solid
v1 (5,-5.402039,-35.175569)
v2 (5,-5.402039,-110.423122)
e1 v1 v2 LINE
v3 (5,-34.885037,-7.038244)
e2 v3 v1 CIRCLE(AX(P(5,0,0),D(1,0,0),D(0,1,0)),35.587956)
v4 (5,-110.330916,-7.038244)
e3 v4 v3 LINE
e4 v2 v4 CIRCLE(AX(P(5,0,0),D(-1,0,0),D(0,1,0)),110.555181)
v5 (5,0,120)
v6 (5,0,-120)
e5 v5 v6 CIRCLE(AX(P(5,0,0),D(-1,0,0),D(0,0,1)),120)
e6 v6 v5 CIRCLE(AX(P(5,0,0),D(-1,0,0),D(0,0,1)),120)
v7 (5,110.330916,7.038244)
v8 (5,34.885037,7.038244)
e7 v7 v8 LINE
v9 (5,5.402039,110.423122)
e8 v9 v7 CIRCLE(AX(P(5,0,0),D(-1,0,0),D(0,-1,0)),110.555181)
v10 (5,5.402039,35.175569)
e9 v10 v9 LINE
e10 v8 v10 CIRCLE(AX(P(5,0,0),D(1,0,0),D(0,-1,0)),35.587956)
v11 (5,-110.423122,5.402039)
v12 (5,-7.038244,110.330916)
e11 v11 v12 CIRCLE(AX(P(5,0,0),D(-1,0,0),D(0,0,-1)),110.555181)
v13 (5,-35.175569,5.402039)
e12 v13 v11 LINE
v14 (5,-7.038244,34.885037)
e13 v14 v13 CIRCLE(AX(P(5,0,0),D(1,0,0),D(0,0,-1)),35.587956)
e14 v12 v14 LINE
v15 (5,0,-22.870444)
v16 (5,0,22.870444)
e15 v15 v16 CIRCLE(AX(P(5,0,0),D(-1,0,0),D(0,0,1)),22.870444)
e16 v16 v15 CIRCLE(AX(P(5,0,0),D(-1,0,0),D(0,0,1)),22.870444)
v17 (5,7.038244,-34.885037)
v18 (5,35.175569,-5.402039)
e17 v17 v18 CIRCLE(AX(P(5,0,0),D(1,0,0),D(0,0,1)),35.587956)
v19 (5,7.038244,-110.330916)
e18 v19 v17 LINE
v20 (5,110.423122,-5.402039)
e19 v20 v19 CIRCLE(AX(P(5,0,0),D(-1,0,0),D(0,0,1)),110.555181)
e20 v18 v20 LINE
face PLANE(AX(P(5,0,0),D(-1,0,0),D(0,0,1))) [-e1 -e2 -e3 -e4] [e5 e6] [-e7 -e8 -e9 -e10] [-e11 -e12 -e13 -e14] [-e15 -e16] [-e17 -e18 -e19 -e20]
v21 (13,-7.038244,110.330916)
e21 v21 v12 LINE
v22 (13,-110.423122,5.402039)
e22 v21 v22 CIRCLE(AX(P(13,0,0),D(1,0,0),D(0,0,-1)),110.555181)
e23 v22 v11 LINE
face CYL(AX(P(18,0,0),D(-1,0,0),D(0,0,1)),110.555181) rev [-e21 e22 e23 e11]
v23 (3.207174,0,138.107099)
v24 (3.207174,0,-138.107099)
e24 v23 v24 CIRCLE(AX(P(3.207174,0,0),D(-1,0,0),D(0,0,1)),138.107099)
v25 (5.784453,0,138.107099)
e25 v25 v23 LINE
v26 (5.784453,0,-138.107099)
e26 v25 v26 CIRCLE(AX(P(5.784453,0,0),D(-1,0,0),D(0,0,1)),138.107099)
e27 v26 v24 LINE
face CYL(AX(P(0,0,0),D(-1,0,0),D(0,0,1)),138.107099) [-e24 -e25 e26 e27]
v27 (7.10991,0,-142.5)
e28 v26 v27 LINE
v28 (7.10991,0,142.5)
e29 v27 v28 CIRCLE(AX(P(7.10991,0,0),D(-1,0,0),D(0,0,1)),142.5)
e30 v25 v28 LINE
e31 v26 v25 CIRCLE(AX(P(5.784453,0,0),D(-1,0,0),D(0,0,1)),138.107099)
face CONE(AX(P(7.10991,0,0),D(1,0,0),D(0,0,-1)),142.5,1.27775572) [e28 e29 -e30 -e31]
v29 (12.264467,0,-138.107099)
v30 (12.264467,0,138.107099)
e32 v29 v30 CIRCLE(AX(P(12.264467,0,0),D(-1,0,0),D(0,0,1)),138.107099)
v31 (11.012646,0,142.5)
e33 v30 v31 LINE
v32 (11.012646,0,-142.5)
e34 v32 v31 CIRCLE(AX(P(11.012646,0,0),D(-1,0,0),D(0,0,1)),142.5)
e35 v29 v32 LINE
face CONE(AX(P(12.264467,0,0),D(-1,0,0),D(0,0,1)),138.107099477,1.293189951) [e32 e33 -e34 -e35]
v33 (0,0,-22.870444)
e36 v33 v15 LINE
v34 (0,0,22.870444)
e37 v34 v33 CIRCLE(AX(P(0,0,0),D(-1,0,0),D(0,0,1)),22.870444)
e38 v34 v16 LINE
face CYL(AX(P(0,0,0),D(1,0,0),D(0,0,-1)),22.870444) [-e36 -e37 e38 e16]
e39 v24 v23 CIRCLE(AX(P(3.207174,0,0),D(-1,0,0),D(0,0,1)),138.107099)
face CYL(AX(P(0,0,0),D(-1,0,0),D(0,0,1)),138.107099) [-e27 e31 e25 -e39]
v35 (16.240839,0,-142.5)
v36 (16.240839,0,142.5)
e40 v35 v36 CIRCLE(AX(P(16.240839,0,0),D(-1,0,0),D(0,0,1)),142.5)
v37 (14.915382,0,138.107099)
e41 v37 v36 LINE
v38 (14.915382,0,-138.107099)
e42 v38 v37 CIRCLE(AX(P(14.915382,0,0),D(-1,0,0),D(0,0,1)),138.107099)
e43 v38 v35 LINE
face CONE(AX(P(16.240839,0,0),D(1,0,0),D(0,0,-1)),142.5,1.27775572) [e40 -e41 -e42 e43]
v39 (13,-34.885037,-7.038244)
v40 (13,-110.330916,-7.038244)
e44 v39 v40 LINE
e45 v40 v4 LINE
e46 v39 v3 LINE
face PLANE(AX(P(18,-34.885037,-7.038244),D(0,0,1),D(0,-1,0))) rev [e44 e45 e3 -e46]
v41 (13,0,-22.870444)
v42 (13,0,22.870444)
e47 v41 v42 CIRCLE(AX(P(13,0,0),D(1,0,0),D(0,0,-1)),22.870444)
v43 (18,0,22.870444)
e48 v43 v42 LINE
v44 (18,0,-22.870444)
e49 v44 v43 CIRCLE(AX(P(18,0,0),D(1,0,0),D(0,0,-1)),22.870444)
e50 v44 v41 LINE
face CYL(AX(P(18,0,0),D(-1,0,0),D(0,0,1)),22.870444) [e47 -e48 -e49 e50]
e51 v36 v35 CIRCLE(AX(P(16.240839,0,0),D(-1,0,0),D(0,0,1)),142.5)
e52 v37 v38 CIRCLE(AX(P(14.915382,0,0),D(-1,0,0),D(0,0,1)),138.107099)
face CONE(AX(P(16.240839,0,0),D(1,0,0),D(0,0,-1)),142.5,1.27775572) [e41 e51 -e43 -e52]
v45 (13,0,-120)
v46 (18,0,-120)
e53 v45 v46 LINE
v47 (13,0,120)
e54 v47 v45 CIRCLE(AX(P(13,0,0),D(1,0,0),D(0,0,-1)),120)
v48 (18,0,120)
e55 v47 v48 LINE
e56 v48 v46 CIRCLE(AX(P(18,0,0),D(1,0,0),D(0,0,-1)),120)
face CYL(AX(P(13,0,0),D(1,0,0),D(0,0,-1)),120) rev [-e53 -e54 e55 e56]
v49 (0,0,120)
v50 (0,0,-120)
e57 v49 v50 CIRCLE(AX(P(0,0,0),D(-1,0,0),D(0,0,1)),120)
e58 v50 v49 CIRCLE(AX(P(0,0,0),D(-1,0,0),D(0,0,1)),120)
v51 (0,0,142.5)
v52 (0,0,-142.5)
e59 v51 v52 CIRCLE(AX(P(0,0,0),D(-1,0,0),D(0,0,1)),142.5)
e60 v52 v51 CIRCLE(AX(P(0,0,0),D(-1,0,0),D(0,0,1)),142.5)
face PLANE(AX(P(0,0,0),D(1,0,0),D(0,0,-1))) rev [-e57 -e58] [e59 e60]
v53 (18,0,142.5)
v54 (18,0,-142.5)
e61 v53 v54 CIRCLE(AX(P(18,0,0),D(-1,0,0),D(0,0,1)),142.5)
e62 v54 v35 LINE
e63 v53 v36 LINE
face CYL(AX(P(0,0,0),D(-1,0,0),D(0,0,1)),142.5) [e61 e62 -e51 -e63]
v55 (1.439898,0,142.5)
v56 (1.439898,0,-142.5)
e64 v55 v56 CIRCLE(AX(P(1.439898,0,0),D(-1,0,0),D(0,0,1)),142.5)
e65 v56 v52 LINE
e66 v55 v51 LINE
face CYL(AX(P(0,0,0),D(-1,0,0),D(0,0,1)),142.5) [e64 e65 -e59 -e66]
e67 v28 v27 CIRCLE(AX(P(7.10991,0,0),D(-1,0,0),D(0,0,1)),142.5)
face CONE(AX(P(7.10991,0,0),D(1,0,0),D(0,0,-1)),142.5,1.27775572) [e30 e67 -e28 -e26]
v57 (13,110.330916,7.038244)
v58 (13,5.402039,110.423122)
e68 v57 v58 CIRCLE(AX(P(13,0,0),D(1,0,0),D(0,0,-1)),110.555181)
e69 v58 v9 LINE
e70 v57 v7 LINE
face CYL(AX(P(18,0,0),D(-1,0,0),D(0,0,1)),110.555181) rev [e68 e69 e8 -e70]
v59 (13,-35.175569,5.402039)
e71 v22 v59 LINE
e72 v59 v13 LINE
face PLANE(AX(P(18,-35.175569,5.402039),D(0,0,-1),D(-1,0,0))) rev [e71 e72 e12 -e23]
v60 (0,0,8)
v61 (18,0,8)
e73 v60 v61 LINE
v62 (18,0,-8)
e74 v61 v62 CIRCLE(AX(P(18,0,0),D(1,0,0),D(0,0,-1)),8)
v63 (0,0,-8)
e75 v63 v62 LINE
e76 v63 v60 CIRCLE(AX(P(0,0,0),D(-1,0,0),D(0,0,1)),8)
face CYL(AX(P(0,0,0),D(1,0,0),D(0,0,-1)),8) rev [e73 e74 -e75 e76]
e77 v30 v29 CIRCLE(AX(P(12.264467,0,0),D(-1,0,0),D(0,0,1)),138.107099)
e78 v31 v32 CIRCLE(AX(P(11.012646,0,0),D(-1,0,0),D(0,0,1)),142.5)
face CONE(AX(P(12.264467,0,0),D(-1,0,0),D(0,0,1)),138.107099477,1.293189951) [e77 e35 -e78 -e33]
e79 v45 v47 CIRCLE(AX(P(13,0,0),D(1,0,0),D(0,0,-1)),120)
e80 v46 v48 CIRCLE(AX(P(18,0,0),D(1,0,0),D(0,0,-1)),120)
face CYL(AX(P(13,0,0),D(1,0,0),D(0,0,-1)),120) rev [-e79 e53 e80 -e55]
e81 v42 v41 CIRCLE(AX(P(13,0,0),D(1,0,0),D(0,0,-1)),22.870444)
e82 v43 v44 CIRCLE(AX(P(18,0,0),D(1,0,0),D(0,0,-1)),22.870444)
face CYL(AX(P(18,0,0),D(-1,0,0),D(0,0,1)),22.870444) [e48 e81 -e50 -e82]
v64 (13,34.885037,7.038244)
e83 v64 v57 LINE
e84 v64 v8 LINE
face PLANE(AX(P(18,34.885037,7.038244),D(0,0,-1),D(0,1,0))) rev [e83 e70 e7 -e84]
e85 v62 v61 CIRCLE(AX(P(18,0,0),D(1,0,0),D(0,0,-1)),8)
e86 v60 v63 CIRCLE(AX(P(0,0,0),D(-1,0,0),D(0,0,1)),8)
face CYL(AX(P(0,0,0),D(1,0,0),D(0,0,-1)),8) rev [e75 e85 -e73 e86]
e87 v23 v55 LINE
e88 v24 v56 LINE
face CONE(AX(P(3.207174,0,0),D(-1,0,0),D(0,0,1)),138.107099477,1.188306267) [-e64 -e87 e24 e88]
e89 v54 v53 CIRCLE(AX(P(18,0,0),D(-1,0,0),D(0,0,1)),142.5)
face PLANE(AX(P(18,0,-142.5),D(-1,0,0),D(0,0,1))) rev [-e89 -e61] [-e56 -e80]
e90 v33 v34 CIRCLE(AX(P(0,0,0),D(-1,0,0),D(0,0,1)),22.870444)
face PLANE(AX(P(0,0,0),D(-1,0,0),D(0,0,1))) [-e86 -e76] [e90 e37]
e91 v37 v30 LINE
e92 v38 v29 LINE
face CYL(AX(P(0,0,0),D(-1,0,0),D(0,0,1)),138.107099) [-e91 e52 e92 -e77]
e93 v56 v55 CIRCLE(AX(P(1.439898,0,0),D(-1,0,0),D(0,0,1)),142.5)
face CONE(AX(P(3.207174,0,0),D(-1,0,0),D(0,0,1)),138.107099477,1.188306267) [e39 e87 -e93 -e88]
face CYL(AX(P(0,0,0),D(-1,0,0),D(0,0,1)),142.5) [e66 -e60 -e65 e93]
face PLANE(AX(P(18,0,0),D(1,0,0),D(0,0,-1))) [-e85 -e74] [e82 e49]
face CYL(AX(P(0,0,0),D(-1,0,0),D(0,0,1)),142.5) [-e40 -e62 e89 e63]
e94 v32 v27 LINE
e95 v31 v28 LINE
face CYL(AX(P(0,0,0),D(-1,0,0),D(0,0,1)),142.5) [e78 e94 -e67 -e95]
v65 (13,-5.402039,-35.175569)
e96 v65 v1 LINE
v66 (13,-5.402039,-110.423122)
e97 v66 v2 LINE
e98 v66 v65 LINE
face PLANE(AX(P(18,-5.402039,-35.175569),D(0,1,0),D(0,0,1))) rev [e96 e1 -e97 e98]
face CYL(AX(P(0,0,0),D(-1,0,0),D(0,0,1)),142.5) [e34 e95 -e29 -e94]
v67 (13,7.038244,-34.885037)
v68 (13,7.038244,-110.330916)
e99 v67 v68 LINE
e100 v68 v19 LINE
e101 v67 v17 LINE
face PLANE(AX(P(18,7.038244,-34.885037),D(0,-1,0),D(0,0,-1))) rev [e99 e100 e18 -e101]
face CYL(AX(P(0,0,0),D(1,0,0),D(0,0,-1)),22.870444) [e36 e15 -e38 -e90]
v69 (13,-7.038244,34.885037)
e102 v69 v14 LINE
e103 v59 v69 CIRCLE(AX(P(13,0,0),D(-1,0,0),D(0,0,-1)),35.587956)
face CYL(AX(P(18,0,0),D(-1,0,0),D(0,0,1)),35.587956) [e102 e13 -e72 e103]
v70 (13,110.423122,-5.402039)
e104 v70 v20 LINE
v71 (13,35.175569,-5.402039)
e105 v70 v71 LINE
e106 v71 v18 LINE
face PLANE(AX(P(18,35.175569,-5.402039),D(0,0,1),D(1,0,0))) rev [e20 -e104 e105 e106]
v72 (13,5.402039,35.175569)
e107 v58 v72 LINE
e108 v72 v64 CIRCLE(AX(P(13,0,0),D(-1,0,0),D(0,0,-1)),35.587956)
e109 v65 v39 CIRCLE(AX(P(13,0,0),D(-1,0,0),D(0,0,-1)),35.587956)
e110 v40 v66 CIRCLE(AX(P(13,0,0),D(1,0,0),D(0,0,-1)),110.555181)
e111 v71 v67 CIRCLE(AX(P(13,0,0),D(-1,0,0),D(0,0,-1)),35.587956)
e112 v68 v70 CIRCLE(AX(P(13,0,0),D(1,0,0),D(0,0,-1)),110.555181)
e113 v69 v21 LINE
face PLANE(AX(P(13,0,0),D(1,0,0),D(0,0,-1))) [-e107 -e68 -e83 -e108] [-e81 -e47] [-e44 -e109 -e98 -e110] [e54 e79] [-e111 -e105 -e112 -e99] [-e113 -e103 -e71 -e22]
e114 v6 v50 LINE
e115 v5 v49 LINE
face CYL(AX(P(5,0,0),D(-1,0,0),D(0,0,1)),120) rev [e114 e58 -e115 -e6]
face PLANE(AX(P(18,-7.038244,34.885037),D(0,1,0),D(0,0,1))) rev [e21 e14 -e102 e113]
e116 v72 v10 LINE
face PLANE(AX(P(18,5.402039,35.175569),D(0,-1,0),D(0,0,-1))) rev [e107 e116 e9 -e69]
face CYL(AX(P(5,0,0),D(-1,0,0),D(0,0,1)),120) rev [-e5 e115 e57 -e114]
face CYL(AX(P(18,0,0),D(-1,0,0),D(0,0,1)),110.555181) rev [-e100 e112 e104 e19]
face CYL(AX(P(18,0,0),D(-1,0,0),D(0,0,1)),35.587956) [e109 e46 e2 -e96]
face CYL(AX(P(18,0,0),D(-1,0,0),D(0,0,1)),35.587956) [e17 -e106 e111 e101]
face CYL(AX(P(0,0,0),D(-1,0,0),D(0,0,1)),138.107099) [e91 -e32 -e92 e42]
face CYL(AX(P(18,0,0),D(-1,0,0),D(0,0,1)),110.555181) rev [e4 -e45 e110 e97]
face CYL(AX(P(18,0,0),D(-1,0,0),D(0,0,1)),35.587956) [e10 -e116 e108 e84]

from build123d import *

# Parameters (mm, degrees)
SKETCH2_R           = 120
CUT_EXTRUDE1_DEPTH  = 5
CUT_EXTRUDE2_START  = -5
SKETCH3_R           = 120
CUT_EXTRUDE2_DEPTH  = 5
SKETCH4_R           = 8
CUT_EXTRUDE3_DEPTH  = 202.944299251
BOSS_EXTRUDE1_START = 5
SKETCH5_R           = 22.870444207
SKETCH5_R_2         = 8
BOSS_EXTRUDE1_DEPTH = 5
SKETCH6_R           = 22.870444207
SKETCH6_R_2         = 8
BOSS_EXTRUDE2_DEPTH = 5
CUT_EXTRUDE5_DEPTH  = 202.944299251
CIRPATTERN1_COUNT   = 4


with BuildPart() as part:
    # Sketch1 → Revolve1 (revolve)
    with BuildSketch(Plane(origin=(0, 0, 0), x_dir=(1, 0, 0), z_dir=(0, 1, 0)), mode=Mode.PRIVATE) as revolve1_sk:
        Polygon((0, 0), (0, 142.5), (1.439897502, 142.5), (3.207174134, 138.107099477), (5.784452556, 138.107099477), (7.10991003, 142.5), (11.012645925, 142.5), (12.264466873, 138.107099477), (14.915381821, 138.107099477), (16.240839295, 142.5), (18, 142.5), (18, 0), align=None)
    revolve(revolve1_sk.sketch.rotate(Axis((0, 0, 0), (1, 0, 0)), 180), axis=Axis((0, 0, 0), (1, 0, 0)))

    # Sketch2 → Cut-Extrude1 (cut)
    with BuildSketch(Plane.ZY):
        Circle(SKETCH2_R)
    extrude(amount=-CUT_EXTRUDE1_DEPTH, mode=Mode.SUBTRACT)

    # Sketch3 → Cut-Extrude2 (cut)
    with BuildSketch(Plane(origin=(18, 0, 0), x_dir=(0, 0, -1), z_dir=(1, 0, 0)).offset(CUT_EXTRUDE2_START)):
        with Locations(Location((0, 0, 0), (0, 0, 180))):
            Circle(SKETCH3_R)
    extrude(amount=CUT_EXTRUDE2_DEPTH, mode=Mode.SUBTRACT)

    # Sketch4 → Cut-Extrude3 (cut, through all)
    with BuildSketch(Plane(origin=(13, 0, 0), x_dir=(0, 0, -1), z_dir=(1, 0, 0))):
        Circle(SKETCH4_R)
    extrude(amount=-CUT_EXTRUDE3_DEPTH, mode=Mode.SUBTRACT)

    # Sketch5 → Boss-Extrude1 (add)
    with BuildSketch(Plane(origin=(13, 0, 0), x_dir=(0, 0, -1), z_dir=(1, 0, 0)).offset(BOSS_EXTRUDE1_START)):
        Circle(SKETCH5_R)
        Circle(SKETCH5_R_2, mode=Mode.SUBTRACT)
    extrude(amount=-BOSS_EXTRUDE1_DEPTH)

    # Sketch6 → Boss-Extrude2 (add)
    with BuildSketch(Plane.ZY.offset(-5)):
        with Locations(Location((0, 0, 0), (0, 0, 180))):
            Circle(SKETCH6_R)
        with Locations(Location((0, 0, 0), (0, 0, 180))):
            Circle(SKETCH6_R_2, mode=Mode.SUBTRACT)
    extrude(amount=BOSS_EXTRUDE2_DEPTH)

    # Sketch7 → Cut-Extrude5 (cut, through all)
    with BuildSketch(Plane.ZY.offset(-5)):
        with BuildLine():
            Line((-5.40203869, 35.175568579), (-5.40203869, 110.423122323))
            ThreePointArc((-5.40203869, 110.423122323), (-77.592767083, 78.751574346), (-110.330916303, 7.038243628))
            Line((-110.330916303, 7.038243628), (-34.885036528, 7.038243628))
            ThreePointArc((-34.885036528, 7.038243628), (-24.57009099, 25.745160237), (-5.40203869, 35.175568579))
        make_face()
    cut_extrude5 = extrude(amount=-CUT_EXTRUDE5_DEPTH, mode=Mode.SUBTRACT)

    # CirPattern1: Cut-Extrude5 ×4 about axis
    cirpattern1_axis = Axis((0, 0, 0), (1, 0, 0))
    for i in range(1, CIRPATTERN1_COUNT):
        add(cut_extrude5.rotate(cirpattern1_axis, i * 360 / CIRPATTERN1_COUNT), mode=Mode.SUBTRACT)


solid = part.part
